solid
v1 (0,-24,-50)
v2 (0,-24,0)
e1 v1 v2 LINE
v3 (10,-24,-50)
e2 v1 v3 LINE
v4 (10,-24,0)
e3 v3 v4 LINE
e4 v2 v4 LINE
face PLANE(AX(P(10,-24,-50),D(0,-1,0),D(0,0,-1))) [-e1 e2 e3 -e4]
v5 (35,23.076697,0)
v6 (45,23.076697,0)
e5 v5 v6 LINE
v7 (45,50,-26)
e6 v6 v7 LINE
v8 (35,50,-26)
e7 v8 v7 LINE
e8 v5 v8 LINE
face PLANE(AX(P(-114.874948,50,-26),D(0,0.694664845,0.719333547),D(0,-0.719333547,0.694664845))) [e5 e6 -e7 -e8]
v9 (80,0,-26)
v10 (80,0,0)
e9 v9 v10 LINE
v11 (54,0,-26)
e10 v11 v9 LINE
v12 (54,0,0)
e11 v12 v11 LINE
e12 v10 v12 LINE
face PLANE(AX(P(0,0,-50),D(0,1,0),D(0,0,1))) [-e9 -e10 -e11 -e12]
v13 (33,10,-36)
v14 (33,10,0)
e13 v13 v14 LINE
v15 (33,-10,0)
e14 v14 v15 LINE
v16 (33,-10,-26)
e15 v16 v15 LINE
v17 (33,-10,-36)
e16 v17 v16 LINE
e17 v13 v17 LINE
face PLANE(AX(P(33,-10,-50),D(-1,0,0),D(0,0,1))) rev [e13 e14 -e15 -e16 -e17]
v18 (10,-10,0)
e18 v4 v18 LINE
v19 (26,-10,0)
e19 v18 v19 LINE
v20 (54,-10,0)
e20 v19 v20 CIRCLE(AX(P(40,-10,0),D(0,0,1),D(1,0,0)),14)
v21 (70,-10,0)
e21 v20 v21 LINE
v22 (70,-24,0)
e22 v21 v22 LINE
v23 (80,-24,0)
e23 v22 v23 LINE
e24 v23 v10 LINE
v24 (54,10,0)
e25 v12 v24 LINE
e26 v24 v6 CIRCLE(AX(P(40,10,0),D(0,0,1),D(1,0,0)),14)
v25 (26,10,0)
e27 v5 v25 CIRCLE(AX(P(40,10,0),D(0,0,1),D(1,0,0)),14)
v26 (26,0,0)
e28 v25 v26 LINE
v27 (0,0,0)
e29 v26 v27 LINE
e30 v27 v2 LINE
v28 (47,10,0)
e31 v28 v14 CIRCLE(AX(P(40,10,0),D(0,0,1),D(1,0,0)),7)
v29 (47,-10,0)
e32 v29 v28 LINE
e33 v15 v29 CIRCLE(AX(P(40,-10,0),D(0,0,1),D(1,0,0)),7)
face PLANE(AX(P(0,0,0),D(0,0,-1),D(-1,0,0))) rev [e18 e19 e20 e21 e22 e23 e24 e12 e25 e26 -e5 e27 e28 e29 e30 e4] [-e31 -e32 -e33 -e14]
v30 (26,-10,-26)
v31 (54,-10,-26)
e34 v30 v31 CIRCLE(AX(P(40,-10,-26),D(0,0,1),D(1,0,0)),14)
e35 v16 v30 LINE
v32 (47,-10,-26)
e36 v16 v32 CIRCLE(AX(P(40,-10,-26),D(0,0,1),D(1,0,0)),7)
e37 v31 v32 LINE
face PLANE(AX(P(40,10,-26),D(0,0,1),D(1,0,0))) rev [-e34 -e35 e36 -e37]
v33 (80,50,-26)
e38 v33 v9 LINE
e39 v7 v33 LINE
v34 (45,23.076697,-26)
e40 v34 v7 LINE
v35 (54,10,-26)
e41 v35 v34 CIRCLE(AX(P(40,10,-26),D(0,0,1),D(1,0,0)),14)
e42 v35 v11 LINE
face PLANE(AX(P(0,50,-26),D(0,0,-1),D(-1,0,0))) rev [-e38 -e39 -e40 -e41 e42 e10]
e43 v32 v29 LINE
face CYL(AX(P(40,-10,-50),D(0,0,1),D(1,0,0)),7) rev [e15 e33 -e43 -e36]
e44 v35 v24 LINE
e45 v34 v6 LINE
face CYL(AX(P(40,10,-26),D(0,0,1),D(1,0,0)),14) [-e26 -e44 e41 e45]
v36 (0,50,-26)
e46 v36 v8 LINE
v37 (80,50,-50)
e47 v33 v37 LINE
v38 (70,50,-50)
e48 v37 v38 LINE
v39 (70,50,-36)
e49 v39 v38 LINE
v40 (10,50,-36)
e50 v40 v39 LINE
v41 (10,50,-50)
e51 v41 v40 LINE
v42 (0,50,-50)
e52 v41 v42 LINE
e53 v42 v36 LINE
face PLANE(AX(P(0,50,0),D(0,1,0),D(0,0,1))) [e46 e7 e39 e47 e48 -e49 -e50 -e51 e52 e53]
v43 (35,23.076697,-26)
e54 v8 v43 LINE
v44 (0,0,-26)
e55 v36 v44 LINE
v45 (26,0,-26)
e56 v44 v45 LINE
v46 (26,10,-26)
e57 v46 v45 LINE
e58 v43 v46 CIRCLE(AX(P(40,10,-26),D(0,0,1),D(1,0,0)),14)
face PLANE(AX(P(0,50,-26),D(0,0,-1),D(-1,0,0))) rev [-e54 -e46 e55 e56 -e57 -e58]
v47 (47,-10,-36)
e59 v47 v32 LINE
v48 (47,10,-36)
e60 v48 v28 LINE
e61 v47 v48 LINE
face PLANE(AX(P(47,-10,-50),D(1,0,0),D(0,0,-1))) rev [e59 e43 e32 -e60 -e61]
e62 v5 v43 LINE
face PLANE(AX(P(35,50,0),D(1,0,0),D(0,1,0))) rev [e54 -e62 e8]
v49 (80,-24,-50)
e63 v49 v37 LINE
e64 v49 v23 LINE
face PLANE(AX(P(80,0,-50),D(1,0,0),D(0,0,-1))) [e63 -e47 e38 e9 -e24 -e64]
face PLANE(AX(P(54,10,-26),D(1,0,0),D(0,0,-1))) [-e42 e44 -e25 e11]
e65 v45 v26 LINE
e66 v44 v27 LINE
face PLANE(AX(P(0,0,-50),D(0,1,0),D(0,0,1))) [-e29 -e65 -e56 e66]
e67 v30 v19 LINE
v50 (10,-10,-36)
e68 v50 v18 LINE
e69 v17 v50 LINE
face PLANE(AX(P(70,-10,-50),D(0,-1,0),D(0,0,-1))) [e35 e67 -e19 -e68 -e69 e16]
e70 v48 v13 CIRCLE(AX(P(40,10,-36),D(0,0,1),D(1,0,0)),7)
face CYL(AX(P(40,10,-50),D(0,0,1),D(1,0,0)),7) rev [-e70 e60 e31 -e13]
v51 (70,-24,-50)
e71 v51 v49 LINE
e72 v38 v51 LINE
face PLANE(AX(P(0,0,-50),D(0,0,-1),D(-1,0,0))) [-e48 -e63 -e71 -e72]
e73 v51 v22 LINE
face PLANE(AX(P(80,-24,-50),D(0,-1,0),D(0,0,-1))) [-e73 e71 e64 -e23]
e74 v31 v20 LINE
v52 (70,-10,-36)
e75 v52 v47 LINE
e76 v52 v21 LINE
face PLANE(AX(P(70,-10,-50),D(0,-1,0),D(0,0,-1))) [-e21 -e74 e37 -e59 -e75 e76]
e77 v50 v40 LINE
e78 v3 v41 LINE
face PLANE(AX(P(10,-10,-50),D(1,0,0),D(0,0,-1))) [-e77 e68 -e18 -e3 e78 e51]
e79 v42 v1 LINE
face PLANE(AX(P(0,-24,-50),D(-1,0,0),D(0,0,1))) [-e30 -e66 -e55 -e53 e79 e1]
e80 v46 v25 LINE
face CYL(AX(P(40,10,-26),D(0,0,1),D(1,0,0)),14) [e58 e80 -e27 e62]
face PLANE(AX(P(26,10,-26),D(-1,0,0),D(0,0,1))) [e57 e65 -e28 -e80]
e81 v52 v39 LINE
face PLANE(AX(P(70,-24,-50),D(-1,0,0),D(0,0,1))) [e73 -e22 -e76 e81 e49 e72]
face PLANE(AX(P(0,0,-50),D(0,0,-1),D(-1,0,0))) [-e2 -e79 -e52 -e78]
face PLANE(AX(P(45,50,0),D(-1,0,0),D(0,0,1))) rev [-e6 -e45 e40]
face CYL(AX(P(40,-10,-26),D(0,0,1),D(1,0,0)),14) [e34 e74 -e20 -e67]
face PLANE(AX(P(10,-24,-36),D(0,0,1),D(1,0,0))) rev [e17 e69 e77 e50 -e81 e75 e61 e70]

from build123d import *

# Parameters (mm, degrees)
BASE_BODY_DEPTH       = 50
BACK_WALL_SKETCH_W    = 80
BACK_WALL_SKETCH_H    = 24
BACK_WALL_DEPTH       = 50
WALL_NOTCH_SKETCH_W   = 60
WALL_NOTCH_SKETCH_H   = 14
WALL_NOTCH_CUT_DEPTH  = 120.899958299
SLOT_BOSS_DEPTH       = 26
SLOT_CUT_14MM_DEPTH   = 107.77078252
RIB_SKETCH_W          = 10
RIB_SKETCH_H          = 27
REINFORCING_RIB_DEPTH = 26
TRIM_CUT_DEPTH        = 84.815273071
TRIM_CUT_DEPTH_BACK   = 26


with BuildPart() as part:
    # Base Profile Sketch → Base Body (new body)
    with BuildSketch(Plane.XY):
        Polygon((0, 0), (40, 0), (80, 0), (80, -24), (70, -24), (70, -10), (10, -10), (10, -24), (0, -24), align=None)
    extrude(amount=-BASE_BODY_DEPTH)

    # Back Wall Sketch → Back Wall (add)
    with BuildSketch(Plane(origin=(0, 0, 0), x_dir=(1, 0, 0), z_dir=(0, 1, 0))):
        with Locations((40, 38)):
            Rectangle(BACK_WALL_SKETCH_W, BACK_WALL_SKETCH_H)
    extrude(amount=BACK_WALL_DEPTH)

    # Wall Notch Sketch → Wall Notch Cut (cut, through all)
    with BuildSketch(Plane(origin=(0, 50, 0), x_dir=(1, 0, 0), z_dir=(0, 1, 0))):
        with Locations((40, 43)):
            Rectangle(WALL_NOTCH_SKETCH_W, WALL_NOTCH_SKETCH_H)
    extrude(amount=-WALL_NOTCH_CUT_DEPTH, mode=Mode.SUBTRACT)

    # Slot Boss Sketch → Slot Boss (add)
    with BuildSketch(Plane.XY):
        with BuildLine():
            Line((26, 10), (26, -10))
            ThreePointArc((26, -10), (40, -24), (54, -10))
            Line((54, -10), (54, 10))
            ThreePointArc((54, 10), (40, 24), (26, 10))
        make_face()
    extrude(amount=-SLOT_BOSS_DEPTH)

    # Slot Sketch → Slot Cut 14mm (cut, through all)
    with BuildSketch(Plane.XY):
        with BuildLine():
            Line((33, -10), (33, 10))
            ThreePointArc((33, 10), (40, 17), (47, 10))
            Line((47, 10), (47, -10))
            ThreePointArc((47, -10), (40, -17), (33, -10))
        make_face()
    extrude(amount=-SLOT_CUT_14MM_DEPTH, mode=Mode.SUBTRACT)

    # Rib Sketch → Reinforcing Rib (add)
    with BuildSketch(Plane.XY.offset(-26)):
        with Locations((40, 36.5)):
            Rectangle(RIB_SKETCH_W, RIB_SKETCH_H)
    extrude(amount=REINFORCING_RIB_DEPTH)

    # Trim Line Sketch → Trim Cut (cut, two sides: drawn at the far end of the back side and taken through both)
    with BuildSketch(Plane.ZY.offset(-35).offset(-TRIM_CUT_DEPTH_BACK)):
        Polygon((-141.918286791, 170.034737621), (-26, 50), (0, 23.076696831), (115.918286791, -96.95804079), (355.987762032, 134.878532791), (98.151188451, 401.871311202), align=None)
    extrude(amount=TRIM_CUT_DEPTH + TRIM_CUT_DEPTH_BACK, mode=Mode.SUBTRACT)


solid = part.part
